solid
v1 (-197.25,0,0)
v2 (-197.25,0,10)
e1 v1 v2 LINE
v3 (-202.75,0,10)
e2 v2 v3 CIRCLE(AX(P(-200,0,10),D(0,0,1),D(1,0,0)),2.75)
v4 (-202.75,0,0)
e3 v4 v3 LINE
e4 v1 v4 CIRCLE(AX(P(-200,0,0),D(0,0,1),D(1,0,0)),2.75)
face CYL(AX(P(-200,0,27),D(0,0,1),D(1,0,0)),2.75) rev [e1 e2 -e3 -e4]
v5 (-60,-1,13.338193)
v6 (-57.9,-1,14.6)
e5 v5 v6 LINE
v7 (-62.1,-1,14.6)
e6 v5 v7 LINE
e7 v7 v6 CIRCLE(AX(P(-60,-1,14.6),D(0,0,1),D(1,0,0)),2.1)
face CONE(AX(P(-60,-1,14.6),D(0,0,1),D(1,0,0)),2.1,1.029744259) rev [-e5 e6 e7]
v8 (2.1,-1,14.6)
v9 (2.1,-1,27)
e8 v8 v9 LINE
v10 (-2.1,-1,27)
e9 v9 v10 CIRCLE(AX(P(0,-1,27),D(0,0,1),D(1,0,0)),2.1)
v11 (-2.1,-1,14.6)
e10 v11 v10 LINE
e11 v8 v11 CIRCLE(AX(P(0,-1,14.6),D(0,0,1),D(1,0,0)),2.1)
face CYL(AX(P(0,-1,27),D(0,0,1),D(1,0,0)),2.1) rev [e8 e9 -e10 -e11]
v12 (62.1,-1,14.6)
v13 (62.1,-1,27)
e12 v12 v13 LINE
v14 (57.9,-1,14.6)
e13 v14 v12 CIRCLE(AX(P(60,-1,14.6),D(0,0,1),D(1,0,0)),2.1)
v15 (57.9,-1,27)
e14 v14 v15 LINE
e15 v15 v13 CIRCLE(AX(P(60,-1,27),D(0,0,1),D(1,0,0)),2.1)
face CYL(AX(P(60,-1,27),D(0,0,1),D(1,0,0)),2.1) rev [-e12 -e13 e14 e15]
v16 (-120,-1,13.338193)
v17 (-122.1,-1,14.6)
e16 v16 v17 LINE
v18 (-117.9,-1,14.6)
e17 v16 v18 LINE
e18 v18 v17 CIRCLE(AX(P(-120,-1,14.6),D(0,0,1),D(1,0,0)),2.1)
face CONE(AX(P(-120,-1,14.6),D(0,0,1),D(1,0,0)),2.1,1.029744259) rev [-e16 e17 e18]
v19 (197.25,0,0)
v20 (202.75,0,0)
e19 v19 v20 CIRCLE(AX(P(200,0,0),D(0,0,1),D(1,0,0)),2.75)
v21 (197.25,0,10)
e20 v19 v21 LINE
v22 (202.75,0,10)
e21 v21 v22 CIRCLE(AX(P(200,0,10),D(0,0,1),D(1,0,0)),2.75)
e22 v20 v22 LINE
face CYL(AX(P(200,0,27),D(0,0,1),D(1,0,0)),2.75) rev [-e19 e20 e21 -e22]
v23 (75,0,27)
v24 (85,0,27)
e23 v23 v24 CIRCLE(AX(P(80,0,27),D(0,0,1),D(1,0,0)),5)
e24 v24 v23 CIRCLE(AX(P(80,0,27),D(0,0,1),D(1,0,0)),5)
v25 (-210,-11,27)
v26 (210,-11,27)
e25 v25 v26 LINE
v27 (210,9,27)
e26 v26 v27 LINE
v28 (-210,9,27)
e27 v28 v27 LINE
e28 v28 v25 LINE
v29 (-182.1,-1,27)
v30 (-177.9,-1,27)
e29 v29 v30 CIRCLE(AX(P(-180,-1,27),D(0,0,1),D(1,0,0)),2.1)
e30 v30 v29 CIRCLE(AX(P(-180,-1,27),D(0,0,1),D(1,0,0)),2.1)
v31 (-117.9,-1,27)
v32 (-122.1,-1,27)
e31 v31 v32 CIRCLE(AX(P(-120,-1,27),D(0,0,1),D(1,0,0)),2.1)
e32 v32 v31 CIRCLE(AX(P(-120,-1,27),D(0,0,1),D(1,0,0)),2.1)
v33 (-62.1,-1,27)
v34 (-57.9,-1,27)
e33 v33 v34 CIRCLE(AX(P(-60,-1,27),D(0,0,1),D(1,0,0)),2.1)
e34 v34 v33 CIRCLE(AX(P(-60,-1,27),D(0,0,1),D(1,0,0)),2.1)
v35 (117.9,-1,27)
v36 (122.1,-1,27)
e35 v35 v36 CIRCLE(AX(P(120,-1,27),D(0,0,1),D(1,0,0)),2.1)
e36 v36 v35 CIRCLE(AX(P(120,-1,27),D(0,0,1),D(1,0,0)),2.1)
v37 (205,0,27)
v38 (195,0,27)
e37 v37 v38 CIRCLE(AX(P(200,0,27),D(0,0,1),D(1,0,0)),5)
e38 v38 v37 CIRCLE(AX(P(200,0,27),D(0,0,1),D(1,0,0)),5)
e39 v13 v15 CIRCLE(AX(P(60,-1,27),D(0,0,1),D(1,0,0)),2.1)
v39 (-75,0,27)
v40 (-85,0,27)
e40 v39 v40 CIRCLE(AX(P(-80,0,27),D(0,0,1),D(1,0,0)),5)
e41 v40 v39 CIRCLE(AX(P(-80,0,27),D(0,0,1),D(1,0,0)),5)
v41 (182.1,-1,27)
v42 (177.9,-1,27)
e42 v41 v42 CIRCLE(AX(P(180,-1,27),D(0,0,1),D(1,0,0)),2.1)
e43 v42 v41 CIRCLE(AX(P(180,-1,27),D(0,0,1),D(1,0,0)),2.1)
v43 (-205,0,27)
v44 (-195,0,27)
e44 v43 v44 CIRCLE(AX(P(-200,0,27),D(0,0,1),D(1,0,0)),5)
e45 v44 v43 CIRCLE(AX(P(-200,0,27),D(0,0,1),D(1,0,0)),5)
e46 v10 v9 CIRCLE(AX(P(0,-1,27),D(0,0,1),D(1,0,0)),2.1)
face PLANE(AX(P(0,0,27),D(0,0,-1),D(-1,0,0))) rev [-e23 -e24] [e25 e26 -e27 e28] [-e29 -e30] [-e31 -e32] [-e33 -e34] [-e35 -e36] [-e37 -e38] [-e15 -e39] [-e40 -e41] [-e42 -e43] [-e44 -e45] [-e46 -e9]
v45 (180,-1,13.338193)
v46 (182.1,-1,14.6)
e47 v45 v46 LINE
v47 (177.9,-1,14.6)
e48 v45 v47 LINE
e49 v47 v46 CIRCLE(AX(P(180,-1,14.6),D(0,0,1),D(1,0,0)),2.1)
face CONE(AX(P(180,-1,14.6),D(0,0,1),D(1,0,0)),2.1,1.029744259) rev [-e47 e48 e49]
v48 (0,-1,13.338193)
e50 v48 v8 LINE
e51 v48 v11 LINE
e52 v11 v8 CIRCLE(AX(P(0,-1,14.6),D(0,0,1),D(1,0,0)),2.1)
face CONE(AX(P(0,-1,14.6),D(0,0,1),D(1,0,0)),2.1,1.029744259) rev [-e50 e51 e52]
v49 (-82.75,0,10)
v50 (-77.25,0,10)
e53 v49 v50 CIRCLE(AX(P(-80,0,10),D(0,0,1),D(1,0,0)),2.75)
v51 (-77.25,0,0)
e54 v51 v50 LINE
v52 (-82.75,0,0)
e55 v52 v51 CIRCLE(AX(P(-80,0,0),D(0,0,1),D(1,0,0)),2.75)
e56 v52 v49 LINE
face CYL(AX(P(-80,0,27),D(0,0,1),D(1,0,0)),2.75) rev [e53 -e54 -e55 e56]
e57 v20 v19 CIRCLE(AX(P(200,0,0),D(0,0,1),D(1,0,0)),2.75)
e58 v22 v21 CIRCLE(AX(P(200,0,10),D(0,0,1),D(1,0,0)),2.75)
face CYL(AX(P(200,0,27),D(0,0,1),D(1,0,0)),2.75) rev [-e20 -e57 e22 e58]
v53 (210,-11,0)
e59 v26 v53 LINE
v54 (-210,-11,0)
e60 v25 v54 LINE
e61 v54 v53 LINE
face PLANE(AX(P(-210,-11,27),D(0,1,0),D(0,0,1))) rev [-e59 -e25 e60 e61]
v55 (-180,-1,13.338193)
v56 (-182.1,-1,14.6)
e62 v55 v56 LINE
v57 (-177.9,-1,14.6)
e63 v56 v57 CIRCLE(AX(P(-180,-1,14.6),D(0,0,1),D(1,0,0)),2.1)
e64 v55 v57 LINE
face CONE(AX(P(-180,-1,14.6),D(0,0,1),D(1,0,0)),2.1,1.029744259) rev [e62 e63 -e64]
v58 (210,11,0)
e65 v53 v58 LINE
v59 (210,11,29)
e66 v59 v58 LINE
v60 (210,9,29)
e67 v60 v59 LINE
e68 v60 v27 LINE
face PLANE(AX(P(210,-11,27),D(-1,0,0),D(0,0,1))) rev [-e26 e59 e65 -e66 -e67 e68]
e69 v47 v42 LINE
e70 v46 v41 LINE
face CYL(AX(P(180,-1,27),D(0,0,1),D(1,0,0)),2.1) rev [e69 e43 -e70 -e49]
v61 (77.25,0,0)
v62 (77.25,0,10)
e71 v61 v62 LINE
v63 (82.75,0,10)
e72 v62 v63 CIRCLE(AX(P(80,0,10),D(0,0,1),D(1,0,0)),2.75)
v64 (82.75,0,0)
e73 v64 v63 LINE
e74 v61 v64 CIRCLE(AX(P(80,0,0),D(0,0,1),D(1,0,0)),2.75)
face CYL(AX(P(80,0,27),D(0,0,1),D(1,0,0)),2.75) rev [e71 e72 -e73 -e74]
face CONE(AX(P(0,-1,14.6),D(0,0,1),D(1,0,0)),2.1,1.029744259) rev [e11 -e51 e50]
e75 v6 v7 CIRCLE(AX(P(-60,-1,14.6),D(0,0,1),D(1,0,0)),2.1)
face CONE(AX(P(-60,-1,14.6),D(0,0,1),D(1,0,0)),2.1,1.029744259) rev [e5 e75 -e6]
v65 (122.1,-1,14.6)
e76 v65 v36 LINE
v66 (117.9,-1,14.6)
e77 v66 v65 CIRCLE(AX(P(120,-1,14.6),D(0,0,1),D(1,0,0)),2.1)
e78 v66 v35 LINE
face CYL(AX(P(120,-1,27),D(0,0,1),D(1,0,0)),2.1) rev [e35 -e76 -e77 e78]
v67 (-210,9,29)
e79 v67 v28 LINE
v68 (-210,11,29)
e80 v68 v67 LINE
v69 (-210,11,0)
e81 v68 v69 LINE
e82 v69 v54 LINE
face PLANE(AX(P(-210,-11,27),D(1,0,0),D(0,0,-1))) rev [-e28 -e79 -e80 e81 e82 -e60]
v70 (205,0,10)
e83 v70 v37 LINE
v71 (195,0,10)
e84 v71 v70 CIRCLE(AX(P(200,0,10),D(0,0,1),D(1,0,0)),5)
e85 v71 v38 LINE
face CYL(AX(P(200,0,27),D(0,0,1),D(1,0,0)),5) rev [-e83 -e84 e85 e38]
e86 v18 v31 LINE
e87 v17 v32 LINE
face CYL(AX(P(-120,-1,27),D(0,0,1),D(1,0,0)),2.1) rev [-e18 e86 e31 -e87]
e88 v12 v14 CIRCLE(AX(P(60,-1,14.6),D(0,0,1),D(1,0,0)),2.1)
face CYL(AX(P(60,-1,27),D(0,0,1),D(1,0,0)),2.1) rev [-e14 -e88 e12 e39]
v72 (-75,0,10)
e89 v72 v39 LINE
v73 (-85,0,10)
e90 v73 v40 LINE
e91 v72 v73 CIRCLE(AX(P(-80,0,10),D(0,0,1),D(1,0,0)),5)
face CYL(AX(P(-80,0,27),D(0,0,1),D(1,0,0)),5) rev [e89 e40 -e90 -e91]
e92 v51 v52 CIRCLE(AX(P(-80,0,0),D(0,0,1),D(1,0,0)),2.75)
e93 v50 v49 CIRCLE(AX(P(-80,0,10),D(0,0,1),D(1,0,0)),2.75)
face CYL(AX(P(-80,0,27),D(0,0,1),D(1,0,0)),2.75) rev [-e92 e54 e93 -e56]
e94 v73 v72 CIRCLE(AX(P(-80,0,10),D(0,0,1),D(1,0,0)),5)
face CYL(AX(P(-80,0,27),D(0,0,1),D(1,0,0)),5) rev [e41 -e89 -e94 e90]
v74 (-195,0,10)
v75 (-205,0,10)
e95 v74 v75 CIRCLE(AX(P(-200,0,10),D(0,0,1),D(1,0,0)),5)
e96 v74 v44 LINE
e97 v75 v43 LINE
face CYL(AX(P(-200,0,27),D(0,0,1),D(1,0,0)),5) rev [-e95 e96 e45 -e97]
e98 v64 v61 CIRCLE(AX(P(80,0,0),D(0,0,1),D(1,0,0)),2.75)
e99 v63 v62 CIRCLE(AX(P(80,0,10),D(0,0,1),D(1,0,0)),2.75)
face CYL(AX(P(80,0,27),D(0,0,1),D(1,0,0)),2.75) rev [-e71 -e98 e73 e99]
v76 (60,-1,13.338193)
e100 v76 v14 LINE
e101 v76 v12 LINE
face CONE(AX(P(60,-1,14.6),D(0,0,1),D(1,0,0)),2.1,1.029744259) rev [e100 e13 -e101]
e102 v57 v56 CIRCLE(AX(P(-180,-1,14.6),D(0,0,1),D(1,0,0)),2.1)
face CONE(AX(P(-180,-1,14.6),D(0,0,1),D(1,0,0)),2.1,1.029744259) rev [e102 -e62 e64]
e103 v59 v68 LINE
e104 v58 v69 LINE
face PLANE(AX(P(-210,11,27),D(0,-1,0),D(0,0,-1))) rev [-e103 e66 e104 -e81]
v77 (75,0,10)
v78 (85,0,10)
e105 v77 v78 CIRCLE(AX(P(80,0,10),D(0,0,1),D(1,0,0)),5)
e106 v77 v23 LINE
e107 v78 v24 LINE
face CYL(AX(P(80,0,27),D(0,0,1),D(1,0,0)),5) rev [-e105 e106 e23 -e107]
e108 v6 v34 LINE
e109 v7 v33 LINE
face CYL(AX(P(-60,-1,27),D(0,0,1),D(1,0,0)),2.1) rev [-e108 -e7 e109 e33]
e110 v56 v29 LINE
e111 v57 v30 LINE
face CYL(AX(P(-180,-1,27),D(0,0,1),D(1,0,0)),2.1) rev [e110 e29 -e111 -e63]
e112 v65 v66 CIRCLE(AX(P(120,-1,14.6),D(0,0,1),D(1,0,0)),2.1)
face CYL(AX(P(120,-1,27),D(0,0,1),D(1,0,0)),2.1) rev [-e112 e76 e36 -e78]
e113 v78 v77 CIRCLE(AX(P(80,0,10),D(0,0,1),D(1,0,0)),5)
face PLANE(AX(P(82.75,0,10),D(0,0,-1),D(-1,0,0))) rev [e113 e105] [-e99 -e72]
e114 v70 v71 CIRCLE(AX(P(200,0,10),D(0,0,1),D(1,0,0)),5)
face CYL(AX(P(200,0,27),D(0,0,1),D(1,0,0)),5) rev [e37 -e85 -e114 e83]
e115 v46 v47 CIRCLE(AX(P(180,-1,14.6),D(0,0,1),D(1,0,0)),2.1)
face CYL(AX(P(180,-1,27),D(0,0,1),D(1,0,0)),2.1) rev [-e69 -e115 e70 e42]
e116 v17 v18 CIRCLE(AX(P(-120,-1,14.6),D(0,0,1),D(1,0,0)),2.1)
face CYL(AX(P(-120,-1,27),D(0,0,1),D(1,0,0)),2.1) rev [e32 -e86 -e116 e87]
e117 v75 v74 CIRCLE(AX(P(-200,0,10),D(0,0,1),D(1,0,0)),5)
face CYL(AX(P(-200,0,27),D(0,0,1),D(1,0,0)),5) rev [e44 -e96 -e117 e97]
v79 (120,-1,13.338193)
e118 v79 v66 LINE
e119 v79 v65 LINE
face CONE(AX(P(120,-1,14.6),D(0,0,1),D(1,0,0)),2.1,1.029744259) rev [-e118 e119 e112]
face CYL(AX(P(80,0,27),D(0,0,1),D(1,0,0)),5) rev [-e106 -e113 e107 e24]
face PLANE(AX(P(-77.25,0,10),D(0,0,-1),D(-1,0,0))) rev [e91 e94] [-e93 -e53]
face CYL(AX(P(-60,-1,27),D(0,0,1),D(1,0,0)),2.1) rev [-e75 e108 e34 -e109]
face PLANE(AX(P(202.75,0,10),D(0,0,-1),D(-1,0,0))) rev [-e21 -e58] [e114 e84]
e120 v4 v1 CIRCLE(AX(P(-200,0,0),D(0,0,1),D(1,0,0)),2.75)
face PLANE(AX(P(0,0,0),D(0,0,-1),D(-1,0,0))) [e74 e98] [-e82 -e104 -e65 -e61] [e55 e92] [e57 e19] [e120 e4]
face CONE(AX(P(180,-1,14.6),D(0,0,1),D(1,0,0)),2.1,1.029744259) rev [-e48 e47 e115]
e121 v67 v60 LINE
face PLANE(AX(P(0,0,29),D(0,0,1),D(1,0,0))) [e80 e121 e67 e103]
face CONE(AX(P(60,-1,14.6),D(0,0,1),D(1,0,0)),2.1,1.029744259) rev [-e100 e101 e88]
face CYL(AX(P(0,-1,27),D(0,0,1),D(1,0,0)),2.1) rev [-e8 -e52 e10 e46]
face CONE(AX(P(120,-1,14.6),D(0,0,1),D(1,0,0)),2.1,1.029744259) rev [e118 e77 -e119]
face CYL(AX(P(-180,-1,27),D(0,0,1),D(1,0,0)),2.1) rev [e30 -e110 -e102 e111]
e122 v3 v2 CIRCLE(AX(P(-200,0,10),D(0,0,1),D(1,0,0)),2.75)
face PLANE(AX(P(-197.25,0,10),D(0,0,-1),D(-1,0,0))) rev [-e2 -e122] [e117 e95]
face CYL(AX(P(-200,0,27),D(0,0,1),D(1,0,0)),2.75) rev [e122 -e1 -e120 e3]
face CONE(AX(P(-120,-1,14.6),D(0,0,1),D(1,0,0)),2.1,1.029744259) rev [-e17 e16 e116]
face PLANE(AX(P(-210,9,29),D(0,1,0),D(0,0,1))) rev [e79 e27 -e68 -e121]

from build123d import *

# Parameters (mm, degrees)
SKETCH1_W                                           = 420
SKETCH1_H                                           = 22
BOSS_EXTRUDE1_DEPTH                                 = 27
SKETCH2_W                                           = 420
SKETCH2_H                                           = 2
BOSS_EXTRUDE2_DEPTH                                 = 2
M5_TAPPED_HOLE1_D                                   = 4.2
M5_TAPPED_HOLE1_DEPTH                               = 12.4
M5_TAPPED_HOLE1_TIP                                 = 1.2618073
CBORE_FOR_M5_HEX_SOCKET_HEAD_CAP_SCREW1_D           = 5.5
CBORE_FOR_M5_HEX_SOCKET_HEAD_CAP_SCREW1_CBORE_D     = 10
CBORE_FOR_M5_HEX_SOCKET_HEAD_CAP_SCREW1_CBORE_DEPTH = 17


with BuildPart() as part:
    # Sketch1 → Boss-Extrude1 (new body)
    with BuildSketch(Plane.XY):
        Rectangle(SKETCH1_W, SKETCH1_H)
    extrude(amount=BOSS_EXTRUDE1_DEPTH)

    # Sketch2 → Boss-Extrude2 (add)
    with BuildSketch(Plane.XY.offset(27)):
        with Locations((0, 10)):
            Rectangle(SKETCH2_W, SKETCH2_H)
    extrude(amount=BOSS_EXTRUDE2_DEPTH)

    # M5 Tapped Hole1
    with Locations(Plane.XY.offset(27)):
        with Locations((180, -1), (120, -1), (60, -1), (0, -1), (-180, -1), (-120, -1), (-60, -1)):
            Hole(M5_TAPPED_HOLE1_D / 2, depth=M5_TAPPED_HOLE1_DEPTH)
            with Locations((0, 0, -(M5_TAPPED_HOLE1_DEPTH + M5_TAPPED_HOLE1_TIP / 2))):  # 118° drill point
                Cone(0, M5_TAPPED_HOLE1_D / 2, M5_TAPPED_HOLE1_TIP, mode=Mode.SUBTRACT)

    # CBORE for M5 Hex Socket Head Cap Screw1 (through all)
    with Locations(Plane.XY.offset(27)):
        with Locations((200, 0), (80, 0), (-80, 0), (-200, 0)):
            CounterBoreHole(CBORE_FOR_M5_HEX_SOCKET_HEAD_CAP_SCREW1_D / 2, CBORE_FOR_M5_HEX_SOCKET_HEAD_CAP_SCREW1_CBORE_D / 2, CBORE_FOR_M5_HEX_SOCKET_HEAD_CAP_SCREW1_CBORE_DEPTH)


solid = part.part
